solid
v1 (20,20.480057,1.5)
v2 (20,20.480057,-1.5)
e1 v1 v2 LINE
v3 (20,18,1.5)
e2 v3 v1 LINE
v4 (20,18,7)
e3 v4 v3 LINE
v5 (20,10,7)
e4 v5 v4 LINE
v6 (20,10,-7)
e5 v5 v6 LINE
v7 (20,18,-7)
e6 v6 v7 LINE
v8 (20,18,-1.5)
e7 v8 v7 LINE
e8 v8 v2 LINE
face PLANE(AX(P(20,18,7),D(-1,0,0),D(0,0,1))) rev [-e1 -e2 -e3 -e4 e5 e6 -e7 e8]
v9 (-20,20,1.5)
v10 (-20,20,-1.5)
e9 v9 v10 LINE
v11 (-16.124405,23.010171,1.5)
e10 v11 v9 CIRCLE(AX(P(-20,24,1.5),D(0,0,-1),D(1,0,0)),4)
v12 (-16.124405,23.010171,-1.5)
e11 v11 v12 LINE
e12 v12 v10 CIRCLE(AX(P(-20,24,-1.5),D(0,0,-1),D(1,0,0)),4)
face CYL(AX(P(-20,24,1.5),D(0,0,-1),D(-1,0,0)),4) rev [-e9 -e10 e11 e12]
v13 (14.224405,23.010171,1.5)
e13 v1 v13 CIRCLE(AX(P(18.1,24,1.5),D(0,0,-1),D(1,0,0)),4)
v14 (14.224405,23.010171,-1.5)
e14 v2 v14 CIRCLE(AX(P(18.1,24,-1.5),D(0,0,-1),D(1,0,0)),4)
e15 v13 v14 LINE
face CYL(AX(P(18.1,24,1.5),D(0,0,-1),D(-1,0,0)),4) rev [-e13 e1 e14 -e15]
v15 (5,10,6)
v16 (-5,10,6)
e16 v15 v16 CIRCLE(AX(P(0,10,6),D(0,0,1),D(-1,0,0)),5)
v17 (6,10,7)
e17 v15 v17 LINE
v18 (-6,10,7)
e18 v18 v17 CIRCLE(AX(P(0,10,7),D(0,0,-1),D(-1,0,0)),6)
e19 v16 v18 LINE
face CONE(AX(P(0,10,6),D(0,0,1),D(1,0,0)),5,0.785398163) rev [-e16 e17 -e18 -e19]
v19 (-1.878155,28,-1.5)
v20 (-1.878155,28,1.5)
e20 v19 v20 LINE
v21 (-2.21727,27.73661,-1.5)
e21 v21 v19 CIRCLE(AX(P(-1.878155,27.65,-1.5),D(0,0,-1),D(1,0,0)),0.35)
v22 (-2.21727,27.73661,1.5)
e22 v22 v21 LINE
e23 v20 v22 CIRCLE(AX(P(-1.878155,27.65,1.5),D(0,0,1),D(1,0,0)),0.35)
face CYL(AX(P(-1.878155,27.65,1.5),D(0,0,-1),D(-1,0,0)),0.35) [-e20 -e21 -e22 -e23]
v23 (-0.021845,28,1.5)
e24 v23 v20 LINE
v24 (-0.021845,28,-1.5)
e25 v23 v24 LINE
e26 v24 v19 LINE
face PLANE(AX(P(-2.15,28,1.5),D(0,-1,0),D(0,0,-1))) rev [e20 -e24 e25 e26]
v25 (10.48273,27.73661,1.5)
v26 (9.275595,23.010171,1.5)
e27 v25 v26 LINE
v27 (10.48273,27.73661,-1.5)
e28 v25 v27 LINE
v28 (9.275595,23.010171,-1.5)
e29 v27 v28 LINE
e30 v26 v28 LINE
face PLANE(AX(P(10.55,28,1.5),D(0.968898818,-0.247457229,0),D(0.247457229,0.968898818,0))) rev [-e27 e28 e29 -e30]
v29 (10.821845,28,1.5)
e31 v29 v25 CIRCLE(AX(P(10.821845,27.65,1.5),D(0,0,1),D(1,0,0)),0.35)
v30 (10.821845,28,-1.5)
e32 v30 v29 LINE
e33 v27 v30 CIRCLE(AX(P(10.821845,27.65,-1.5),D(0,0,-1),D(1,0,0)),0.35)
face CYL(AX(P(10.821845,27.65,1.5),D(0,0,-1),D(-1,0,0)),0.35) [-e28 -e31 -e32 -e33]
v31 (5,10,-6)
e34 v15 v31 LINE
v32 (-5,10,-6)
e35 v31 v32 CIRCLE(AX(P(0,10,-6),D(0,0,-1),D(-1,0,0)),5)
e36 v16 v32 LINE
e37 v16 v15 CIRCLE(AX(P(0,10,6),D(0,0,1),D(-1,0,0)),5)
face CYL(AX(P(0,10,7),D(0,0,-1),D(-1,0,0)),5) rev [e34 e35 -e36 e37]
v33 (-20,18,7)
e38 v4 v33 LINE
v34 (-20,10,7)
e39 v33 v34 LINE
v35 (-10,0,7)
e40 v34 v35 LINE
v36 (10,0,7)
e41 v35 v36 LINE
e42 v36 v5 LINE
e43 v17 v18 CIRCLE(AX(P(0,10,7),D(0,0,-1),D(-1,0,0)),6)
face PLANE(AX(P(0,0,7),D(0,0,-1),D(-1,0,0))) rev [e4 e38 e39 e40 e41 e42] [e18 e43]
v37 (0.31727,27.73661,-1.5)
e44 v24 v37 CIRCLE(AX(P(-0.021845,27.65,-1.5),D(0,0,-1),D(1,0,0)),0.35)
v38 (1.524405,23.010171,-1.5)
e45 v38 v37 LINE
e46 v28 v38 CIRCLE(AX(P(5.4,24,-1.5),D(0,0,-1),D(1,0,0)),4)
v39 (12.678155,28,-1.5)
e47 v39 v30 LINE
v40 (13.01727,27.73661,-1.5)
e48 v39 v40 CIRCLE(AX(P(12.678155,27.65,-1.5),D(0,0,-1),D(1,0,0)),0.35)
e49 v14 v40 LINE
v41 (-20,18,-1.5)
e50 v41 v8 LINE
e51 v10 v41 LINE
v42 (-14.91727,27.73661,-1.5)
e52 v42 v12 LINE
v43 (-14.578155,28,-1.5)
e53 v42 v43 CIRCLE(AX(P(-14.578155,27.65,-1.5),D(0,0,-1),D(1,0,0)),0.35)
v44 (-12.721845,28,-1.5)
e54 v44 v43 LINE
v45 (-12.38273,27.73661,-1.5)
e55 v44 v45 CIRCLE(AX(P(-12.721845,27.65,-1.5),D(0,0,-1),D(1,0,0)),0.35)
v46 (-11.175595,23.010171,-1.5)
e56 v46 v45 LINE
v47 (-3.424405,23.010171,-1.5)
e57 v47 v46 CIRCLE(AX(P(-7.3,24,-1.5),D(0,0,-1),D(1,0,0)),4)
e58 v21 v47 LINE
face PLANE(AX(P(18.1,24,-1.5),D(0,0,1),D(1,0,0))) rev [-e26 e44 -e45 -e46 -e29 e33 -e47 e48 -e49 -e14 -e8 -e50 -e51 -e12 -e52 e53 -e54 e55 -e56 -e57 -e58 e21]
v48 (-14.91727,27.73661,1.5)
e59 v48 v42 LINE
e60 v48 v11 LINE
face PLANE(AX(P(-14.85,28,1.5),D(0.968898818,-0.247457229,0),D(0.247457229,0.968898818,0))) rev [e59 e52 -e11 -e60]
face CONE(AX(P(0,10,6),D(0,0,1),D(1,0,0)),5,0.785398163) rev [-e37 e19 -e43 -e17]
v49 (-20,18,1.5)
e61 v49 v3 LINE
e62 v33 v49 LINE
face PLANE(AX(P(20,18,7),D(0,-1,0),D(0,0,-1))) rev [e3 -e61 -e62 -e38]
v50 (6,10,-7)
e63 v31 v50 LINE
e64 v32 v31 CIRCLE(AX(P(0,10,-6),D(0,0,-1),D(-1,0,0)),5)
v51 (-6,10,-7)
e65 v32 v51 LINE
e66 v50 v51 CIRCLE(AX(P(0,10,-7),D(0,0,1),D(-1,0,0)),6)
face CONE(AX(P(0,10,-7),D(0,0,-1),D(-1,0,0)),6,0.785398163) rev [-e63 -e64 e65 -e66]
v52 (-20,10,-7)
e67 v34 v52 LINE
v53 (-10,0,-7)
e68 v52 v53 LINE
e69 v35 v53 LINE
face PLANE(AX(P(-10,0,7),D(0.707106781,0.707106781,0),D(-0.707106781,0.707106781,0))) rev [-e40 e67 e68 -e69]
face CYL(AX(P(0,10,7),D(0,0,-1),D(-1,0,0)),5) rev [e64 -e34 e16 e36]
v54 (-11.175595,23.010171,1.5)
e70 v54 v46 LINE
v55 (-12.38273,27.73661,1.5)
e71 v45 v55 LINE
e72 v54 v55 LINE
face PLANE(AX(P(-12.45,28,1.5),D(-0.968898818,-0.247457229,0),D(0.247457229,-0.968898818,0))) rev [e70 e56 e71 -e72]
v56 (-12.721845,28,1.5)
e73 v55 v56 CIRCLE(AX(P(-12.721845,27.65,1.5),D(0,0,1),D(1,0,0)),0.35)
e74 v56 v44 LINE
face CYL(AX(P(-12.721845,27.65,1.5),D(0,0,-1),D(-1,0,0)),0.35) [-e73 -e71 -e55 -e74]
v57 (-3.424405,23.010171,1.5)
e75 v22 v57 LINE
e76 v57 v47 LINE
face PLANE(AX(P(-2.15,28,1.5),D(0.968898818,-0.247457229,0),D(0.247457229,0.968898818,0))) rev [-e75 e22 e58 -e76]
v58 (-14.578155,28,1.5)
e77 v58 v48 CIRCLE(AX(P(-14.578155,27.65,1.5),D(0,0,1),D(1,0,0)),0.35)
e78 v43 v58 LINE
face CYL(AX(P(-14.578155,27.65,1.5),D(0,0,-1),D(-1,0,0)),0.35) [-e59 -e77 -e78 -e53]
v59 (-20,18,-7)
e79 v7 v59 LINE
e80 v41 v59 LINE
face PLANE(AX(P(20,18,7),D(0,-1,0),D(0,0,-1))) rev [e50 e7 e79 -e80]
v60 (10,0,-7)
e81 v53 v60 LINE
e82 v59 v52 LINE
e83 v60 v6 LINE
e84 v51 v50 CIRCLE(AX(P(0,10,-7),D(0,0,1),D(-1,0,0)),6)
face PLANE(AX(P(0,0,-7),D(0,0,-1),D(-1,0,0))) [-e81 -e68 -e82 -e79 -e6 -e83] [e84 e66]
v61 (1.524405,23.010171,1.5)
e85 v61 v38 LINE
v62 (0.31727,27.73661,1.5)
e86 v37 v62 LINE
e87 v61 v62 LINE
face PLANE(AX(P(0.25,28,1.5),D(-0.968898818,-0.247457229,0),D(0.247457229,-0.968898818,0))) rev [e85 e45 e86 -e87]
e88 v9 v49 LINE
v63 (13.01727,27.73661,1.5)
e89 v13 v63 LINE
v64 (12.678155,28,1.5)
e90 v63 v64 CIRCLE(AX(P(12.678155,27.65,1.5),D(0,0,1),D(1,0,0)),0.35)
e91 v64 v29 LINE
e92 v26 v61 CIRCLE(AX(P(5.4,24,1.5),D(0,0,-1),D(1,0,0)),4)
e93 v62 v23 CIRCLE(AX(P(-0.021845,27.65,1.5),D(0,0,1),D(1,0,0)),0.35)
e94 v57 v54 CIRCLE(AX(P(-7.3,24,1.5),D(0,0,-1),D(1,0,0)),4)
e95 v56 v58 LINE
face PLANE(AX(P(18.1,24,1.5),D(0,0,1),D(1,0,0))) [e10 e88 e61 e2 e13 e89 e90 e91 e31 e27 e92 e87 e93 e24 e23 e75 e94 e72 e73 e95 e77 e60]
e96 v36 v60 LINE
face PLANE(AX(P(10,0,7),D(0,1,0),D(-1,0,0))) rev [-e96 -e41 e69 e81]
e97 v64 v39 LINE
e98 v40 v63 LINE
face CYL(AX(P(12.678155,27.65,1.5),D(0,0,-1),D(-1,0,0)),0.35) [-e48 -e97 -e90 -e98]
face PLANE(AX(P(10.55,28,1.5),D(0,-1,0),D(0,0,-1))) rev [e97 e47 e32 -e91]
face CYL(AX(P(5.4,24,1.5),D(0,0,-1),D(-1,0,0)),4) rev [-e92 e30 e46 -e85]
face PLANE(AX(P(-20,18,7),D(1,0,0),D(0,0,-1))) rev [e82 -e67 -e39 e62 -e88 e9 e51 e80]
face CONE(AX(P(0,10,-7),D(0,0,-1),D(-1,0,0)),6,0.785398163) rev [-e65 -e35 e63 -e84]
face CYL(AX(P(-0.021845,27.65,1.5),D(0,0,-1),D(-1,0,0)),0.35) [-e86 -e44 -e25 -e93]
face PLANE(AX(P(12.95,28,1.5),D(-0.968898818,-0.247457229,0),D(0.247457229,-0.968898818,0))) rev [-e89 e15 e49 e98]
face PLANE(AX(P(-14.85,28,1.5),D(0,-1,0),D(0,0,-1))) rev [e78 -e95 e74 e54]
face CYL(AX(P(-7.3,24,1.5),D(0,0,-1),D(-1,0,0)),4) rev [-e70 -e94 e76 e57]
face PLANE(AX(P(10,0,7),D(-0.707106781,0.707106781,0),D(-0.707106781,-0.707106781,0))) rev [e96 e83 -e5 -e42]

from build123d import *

# Parameters (mm, degrees)
SKETCH_1_R      = 5
EXTRUDE_1_DEPTH = 7
EXTRUDE_2_DEPTH = 1.5
FILLET_1_R      = 0.35
CHAMFER_1_SIZE  = 1


with BuildPart() as part:
    # 草图1 → 凸台-拉伸1 (new, symmetric)
    with BuildSketch(Plane.XY):
        Polygon((20, 18), (-20, 18), (-20, 10), (-10, 0), (10, 0), (20, 10), align=None)
        with Locations((0, 10)):
            Circle(SKETCH_1_R, mode=Mode.SUBTRACT)
    extrude(amount=EXTRUDE_1_DEPTH, both=True)

    # 草图2 → 凸台-拉伸2 (add, symmetric)
    with BuildSketch(Plane.XY):
        with BuildLine():
            Line((-14.85, 28), (-12.45, 28))
            Line((-12.45, 28), (-11.175595273, 23.010171086))
            ThreePointArc((-11.175595273, 23.010171086), (-7.3, 20), (-3.424404727, 23.010171086))
            Line((-3.424404727, 23.010171086), (-2.15, 28))
            Line((-2.15, 28), (0.25, 28))
            Line((0.25, 28), (1.524404727, 23.010171086))
            ThreePointArc((1.524404727, 23.010171086), (5.4, 20), (9.275595273, 23.010171086))
            Line((9.275595273, 23.010171086), (10.55, 28))
            Line((10.55, 28), (12.95, 28))
            Line((12.95, 28), (14.224404727, 23.010171086))
            ThreePointArc((14.224404727, 23.010171086), (16.494972361, 20.336137792), (20, 20.480056819))
            Line((20, 20.480056819), (20, 18))
            Line((20, 18), (-20, 18))
            Line((-20, 18), (-20, 20))
            ThreePointArc((-20, 20), (-17.546361442, 20.840940357), (-16.124404727, 23.010171086))
            Line((-16.124404727, 23.010171086), (-14.85, 28))
        make_face()
    extrude(amount=EXTRUDE_2_DEPTH, both=True)

    # 圆角1
    fillet_1_edges = [part.edges().sort_by_distance(p)[0] for p in [
        (12.95, 28, 0),
        (10.55, 28, 0),
        (0.25, 28, 0),
        (-2.15, 28, 0),
        (-12.45, 28, 0),
        (-14.85, 28, 0),
    ]]
    fillet(fillet_1_edges, radius=FILLET_1_R)

    # 倒角1
    chamfer_1_edges = [part.edges().sort_by_distance(p)[0] for p in [
        (-5, 10, -7),
        (-5, 10, 7),
    ]]
    chamfer(chamfer_1_edges, length=CHAMFER_1_SIZE)


solid = part.part
